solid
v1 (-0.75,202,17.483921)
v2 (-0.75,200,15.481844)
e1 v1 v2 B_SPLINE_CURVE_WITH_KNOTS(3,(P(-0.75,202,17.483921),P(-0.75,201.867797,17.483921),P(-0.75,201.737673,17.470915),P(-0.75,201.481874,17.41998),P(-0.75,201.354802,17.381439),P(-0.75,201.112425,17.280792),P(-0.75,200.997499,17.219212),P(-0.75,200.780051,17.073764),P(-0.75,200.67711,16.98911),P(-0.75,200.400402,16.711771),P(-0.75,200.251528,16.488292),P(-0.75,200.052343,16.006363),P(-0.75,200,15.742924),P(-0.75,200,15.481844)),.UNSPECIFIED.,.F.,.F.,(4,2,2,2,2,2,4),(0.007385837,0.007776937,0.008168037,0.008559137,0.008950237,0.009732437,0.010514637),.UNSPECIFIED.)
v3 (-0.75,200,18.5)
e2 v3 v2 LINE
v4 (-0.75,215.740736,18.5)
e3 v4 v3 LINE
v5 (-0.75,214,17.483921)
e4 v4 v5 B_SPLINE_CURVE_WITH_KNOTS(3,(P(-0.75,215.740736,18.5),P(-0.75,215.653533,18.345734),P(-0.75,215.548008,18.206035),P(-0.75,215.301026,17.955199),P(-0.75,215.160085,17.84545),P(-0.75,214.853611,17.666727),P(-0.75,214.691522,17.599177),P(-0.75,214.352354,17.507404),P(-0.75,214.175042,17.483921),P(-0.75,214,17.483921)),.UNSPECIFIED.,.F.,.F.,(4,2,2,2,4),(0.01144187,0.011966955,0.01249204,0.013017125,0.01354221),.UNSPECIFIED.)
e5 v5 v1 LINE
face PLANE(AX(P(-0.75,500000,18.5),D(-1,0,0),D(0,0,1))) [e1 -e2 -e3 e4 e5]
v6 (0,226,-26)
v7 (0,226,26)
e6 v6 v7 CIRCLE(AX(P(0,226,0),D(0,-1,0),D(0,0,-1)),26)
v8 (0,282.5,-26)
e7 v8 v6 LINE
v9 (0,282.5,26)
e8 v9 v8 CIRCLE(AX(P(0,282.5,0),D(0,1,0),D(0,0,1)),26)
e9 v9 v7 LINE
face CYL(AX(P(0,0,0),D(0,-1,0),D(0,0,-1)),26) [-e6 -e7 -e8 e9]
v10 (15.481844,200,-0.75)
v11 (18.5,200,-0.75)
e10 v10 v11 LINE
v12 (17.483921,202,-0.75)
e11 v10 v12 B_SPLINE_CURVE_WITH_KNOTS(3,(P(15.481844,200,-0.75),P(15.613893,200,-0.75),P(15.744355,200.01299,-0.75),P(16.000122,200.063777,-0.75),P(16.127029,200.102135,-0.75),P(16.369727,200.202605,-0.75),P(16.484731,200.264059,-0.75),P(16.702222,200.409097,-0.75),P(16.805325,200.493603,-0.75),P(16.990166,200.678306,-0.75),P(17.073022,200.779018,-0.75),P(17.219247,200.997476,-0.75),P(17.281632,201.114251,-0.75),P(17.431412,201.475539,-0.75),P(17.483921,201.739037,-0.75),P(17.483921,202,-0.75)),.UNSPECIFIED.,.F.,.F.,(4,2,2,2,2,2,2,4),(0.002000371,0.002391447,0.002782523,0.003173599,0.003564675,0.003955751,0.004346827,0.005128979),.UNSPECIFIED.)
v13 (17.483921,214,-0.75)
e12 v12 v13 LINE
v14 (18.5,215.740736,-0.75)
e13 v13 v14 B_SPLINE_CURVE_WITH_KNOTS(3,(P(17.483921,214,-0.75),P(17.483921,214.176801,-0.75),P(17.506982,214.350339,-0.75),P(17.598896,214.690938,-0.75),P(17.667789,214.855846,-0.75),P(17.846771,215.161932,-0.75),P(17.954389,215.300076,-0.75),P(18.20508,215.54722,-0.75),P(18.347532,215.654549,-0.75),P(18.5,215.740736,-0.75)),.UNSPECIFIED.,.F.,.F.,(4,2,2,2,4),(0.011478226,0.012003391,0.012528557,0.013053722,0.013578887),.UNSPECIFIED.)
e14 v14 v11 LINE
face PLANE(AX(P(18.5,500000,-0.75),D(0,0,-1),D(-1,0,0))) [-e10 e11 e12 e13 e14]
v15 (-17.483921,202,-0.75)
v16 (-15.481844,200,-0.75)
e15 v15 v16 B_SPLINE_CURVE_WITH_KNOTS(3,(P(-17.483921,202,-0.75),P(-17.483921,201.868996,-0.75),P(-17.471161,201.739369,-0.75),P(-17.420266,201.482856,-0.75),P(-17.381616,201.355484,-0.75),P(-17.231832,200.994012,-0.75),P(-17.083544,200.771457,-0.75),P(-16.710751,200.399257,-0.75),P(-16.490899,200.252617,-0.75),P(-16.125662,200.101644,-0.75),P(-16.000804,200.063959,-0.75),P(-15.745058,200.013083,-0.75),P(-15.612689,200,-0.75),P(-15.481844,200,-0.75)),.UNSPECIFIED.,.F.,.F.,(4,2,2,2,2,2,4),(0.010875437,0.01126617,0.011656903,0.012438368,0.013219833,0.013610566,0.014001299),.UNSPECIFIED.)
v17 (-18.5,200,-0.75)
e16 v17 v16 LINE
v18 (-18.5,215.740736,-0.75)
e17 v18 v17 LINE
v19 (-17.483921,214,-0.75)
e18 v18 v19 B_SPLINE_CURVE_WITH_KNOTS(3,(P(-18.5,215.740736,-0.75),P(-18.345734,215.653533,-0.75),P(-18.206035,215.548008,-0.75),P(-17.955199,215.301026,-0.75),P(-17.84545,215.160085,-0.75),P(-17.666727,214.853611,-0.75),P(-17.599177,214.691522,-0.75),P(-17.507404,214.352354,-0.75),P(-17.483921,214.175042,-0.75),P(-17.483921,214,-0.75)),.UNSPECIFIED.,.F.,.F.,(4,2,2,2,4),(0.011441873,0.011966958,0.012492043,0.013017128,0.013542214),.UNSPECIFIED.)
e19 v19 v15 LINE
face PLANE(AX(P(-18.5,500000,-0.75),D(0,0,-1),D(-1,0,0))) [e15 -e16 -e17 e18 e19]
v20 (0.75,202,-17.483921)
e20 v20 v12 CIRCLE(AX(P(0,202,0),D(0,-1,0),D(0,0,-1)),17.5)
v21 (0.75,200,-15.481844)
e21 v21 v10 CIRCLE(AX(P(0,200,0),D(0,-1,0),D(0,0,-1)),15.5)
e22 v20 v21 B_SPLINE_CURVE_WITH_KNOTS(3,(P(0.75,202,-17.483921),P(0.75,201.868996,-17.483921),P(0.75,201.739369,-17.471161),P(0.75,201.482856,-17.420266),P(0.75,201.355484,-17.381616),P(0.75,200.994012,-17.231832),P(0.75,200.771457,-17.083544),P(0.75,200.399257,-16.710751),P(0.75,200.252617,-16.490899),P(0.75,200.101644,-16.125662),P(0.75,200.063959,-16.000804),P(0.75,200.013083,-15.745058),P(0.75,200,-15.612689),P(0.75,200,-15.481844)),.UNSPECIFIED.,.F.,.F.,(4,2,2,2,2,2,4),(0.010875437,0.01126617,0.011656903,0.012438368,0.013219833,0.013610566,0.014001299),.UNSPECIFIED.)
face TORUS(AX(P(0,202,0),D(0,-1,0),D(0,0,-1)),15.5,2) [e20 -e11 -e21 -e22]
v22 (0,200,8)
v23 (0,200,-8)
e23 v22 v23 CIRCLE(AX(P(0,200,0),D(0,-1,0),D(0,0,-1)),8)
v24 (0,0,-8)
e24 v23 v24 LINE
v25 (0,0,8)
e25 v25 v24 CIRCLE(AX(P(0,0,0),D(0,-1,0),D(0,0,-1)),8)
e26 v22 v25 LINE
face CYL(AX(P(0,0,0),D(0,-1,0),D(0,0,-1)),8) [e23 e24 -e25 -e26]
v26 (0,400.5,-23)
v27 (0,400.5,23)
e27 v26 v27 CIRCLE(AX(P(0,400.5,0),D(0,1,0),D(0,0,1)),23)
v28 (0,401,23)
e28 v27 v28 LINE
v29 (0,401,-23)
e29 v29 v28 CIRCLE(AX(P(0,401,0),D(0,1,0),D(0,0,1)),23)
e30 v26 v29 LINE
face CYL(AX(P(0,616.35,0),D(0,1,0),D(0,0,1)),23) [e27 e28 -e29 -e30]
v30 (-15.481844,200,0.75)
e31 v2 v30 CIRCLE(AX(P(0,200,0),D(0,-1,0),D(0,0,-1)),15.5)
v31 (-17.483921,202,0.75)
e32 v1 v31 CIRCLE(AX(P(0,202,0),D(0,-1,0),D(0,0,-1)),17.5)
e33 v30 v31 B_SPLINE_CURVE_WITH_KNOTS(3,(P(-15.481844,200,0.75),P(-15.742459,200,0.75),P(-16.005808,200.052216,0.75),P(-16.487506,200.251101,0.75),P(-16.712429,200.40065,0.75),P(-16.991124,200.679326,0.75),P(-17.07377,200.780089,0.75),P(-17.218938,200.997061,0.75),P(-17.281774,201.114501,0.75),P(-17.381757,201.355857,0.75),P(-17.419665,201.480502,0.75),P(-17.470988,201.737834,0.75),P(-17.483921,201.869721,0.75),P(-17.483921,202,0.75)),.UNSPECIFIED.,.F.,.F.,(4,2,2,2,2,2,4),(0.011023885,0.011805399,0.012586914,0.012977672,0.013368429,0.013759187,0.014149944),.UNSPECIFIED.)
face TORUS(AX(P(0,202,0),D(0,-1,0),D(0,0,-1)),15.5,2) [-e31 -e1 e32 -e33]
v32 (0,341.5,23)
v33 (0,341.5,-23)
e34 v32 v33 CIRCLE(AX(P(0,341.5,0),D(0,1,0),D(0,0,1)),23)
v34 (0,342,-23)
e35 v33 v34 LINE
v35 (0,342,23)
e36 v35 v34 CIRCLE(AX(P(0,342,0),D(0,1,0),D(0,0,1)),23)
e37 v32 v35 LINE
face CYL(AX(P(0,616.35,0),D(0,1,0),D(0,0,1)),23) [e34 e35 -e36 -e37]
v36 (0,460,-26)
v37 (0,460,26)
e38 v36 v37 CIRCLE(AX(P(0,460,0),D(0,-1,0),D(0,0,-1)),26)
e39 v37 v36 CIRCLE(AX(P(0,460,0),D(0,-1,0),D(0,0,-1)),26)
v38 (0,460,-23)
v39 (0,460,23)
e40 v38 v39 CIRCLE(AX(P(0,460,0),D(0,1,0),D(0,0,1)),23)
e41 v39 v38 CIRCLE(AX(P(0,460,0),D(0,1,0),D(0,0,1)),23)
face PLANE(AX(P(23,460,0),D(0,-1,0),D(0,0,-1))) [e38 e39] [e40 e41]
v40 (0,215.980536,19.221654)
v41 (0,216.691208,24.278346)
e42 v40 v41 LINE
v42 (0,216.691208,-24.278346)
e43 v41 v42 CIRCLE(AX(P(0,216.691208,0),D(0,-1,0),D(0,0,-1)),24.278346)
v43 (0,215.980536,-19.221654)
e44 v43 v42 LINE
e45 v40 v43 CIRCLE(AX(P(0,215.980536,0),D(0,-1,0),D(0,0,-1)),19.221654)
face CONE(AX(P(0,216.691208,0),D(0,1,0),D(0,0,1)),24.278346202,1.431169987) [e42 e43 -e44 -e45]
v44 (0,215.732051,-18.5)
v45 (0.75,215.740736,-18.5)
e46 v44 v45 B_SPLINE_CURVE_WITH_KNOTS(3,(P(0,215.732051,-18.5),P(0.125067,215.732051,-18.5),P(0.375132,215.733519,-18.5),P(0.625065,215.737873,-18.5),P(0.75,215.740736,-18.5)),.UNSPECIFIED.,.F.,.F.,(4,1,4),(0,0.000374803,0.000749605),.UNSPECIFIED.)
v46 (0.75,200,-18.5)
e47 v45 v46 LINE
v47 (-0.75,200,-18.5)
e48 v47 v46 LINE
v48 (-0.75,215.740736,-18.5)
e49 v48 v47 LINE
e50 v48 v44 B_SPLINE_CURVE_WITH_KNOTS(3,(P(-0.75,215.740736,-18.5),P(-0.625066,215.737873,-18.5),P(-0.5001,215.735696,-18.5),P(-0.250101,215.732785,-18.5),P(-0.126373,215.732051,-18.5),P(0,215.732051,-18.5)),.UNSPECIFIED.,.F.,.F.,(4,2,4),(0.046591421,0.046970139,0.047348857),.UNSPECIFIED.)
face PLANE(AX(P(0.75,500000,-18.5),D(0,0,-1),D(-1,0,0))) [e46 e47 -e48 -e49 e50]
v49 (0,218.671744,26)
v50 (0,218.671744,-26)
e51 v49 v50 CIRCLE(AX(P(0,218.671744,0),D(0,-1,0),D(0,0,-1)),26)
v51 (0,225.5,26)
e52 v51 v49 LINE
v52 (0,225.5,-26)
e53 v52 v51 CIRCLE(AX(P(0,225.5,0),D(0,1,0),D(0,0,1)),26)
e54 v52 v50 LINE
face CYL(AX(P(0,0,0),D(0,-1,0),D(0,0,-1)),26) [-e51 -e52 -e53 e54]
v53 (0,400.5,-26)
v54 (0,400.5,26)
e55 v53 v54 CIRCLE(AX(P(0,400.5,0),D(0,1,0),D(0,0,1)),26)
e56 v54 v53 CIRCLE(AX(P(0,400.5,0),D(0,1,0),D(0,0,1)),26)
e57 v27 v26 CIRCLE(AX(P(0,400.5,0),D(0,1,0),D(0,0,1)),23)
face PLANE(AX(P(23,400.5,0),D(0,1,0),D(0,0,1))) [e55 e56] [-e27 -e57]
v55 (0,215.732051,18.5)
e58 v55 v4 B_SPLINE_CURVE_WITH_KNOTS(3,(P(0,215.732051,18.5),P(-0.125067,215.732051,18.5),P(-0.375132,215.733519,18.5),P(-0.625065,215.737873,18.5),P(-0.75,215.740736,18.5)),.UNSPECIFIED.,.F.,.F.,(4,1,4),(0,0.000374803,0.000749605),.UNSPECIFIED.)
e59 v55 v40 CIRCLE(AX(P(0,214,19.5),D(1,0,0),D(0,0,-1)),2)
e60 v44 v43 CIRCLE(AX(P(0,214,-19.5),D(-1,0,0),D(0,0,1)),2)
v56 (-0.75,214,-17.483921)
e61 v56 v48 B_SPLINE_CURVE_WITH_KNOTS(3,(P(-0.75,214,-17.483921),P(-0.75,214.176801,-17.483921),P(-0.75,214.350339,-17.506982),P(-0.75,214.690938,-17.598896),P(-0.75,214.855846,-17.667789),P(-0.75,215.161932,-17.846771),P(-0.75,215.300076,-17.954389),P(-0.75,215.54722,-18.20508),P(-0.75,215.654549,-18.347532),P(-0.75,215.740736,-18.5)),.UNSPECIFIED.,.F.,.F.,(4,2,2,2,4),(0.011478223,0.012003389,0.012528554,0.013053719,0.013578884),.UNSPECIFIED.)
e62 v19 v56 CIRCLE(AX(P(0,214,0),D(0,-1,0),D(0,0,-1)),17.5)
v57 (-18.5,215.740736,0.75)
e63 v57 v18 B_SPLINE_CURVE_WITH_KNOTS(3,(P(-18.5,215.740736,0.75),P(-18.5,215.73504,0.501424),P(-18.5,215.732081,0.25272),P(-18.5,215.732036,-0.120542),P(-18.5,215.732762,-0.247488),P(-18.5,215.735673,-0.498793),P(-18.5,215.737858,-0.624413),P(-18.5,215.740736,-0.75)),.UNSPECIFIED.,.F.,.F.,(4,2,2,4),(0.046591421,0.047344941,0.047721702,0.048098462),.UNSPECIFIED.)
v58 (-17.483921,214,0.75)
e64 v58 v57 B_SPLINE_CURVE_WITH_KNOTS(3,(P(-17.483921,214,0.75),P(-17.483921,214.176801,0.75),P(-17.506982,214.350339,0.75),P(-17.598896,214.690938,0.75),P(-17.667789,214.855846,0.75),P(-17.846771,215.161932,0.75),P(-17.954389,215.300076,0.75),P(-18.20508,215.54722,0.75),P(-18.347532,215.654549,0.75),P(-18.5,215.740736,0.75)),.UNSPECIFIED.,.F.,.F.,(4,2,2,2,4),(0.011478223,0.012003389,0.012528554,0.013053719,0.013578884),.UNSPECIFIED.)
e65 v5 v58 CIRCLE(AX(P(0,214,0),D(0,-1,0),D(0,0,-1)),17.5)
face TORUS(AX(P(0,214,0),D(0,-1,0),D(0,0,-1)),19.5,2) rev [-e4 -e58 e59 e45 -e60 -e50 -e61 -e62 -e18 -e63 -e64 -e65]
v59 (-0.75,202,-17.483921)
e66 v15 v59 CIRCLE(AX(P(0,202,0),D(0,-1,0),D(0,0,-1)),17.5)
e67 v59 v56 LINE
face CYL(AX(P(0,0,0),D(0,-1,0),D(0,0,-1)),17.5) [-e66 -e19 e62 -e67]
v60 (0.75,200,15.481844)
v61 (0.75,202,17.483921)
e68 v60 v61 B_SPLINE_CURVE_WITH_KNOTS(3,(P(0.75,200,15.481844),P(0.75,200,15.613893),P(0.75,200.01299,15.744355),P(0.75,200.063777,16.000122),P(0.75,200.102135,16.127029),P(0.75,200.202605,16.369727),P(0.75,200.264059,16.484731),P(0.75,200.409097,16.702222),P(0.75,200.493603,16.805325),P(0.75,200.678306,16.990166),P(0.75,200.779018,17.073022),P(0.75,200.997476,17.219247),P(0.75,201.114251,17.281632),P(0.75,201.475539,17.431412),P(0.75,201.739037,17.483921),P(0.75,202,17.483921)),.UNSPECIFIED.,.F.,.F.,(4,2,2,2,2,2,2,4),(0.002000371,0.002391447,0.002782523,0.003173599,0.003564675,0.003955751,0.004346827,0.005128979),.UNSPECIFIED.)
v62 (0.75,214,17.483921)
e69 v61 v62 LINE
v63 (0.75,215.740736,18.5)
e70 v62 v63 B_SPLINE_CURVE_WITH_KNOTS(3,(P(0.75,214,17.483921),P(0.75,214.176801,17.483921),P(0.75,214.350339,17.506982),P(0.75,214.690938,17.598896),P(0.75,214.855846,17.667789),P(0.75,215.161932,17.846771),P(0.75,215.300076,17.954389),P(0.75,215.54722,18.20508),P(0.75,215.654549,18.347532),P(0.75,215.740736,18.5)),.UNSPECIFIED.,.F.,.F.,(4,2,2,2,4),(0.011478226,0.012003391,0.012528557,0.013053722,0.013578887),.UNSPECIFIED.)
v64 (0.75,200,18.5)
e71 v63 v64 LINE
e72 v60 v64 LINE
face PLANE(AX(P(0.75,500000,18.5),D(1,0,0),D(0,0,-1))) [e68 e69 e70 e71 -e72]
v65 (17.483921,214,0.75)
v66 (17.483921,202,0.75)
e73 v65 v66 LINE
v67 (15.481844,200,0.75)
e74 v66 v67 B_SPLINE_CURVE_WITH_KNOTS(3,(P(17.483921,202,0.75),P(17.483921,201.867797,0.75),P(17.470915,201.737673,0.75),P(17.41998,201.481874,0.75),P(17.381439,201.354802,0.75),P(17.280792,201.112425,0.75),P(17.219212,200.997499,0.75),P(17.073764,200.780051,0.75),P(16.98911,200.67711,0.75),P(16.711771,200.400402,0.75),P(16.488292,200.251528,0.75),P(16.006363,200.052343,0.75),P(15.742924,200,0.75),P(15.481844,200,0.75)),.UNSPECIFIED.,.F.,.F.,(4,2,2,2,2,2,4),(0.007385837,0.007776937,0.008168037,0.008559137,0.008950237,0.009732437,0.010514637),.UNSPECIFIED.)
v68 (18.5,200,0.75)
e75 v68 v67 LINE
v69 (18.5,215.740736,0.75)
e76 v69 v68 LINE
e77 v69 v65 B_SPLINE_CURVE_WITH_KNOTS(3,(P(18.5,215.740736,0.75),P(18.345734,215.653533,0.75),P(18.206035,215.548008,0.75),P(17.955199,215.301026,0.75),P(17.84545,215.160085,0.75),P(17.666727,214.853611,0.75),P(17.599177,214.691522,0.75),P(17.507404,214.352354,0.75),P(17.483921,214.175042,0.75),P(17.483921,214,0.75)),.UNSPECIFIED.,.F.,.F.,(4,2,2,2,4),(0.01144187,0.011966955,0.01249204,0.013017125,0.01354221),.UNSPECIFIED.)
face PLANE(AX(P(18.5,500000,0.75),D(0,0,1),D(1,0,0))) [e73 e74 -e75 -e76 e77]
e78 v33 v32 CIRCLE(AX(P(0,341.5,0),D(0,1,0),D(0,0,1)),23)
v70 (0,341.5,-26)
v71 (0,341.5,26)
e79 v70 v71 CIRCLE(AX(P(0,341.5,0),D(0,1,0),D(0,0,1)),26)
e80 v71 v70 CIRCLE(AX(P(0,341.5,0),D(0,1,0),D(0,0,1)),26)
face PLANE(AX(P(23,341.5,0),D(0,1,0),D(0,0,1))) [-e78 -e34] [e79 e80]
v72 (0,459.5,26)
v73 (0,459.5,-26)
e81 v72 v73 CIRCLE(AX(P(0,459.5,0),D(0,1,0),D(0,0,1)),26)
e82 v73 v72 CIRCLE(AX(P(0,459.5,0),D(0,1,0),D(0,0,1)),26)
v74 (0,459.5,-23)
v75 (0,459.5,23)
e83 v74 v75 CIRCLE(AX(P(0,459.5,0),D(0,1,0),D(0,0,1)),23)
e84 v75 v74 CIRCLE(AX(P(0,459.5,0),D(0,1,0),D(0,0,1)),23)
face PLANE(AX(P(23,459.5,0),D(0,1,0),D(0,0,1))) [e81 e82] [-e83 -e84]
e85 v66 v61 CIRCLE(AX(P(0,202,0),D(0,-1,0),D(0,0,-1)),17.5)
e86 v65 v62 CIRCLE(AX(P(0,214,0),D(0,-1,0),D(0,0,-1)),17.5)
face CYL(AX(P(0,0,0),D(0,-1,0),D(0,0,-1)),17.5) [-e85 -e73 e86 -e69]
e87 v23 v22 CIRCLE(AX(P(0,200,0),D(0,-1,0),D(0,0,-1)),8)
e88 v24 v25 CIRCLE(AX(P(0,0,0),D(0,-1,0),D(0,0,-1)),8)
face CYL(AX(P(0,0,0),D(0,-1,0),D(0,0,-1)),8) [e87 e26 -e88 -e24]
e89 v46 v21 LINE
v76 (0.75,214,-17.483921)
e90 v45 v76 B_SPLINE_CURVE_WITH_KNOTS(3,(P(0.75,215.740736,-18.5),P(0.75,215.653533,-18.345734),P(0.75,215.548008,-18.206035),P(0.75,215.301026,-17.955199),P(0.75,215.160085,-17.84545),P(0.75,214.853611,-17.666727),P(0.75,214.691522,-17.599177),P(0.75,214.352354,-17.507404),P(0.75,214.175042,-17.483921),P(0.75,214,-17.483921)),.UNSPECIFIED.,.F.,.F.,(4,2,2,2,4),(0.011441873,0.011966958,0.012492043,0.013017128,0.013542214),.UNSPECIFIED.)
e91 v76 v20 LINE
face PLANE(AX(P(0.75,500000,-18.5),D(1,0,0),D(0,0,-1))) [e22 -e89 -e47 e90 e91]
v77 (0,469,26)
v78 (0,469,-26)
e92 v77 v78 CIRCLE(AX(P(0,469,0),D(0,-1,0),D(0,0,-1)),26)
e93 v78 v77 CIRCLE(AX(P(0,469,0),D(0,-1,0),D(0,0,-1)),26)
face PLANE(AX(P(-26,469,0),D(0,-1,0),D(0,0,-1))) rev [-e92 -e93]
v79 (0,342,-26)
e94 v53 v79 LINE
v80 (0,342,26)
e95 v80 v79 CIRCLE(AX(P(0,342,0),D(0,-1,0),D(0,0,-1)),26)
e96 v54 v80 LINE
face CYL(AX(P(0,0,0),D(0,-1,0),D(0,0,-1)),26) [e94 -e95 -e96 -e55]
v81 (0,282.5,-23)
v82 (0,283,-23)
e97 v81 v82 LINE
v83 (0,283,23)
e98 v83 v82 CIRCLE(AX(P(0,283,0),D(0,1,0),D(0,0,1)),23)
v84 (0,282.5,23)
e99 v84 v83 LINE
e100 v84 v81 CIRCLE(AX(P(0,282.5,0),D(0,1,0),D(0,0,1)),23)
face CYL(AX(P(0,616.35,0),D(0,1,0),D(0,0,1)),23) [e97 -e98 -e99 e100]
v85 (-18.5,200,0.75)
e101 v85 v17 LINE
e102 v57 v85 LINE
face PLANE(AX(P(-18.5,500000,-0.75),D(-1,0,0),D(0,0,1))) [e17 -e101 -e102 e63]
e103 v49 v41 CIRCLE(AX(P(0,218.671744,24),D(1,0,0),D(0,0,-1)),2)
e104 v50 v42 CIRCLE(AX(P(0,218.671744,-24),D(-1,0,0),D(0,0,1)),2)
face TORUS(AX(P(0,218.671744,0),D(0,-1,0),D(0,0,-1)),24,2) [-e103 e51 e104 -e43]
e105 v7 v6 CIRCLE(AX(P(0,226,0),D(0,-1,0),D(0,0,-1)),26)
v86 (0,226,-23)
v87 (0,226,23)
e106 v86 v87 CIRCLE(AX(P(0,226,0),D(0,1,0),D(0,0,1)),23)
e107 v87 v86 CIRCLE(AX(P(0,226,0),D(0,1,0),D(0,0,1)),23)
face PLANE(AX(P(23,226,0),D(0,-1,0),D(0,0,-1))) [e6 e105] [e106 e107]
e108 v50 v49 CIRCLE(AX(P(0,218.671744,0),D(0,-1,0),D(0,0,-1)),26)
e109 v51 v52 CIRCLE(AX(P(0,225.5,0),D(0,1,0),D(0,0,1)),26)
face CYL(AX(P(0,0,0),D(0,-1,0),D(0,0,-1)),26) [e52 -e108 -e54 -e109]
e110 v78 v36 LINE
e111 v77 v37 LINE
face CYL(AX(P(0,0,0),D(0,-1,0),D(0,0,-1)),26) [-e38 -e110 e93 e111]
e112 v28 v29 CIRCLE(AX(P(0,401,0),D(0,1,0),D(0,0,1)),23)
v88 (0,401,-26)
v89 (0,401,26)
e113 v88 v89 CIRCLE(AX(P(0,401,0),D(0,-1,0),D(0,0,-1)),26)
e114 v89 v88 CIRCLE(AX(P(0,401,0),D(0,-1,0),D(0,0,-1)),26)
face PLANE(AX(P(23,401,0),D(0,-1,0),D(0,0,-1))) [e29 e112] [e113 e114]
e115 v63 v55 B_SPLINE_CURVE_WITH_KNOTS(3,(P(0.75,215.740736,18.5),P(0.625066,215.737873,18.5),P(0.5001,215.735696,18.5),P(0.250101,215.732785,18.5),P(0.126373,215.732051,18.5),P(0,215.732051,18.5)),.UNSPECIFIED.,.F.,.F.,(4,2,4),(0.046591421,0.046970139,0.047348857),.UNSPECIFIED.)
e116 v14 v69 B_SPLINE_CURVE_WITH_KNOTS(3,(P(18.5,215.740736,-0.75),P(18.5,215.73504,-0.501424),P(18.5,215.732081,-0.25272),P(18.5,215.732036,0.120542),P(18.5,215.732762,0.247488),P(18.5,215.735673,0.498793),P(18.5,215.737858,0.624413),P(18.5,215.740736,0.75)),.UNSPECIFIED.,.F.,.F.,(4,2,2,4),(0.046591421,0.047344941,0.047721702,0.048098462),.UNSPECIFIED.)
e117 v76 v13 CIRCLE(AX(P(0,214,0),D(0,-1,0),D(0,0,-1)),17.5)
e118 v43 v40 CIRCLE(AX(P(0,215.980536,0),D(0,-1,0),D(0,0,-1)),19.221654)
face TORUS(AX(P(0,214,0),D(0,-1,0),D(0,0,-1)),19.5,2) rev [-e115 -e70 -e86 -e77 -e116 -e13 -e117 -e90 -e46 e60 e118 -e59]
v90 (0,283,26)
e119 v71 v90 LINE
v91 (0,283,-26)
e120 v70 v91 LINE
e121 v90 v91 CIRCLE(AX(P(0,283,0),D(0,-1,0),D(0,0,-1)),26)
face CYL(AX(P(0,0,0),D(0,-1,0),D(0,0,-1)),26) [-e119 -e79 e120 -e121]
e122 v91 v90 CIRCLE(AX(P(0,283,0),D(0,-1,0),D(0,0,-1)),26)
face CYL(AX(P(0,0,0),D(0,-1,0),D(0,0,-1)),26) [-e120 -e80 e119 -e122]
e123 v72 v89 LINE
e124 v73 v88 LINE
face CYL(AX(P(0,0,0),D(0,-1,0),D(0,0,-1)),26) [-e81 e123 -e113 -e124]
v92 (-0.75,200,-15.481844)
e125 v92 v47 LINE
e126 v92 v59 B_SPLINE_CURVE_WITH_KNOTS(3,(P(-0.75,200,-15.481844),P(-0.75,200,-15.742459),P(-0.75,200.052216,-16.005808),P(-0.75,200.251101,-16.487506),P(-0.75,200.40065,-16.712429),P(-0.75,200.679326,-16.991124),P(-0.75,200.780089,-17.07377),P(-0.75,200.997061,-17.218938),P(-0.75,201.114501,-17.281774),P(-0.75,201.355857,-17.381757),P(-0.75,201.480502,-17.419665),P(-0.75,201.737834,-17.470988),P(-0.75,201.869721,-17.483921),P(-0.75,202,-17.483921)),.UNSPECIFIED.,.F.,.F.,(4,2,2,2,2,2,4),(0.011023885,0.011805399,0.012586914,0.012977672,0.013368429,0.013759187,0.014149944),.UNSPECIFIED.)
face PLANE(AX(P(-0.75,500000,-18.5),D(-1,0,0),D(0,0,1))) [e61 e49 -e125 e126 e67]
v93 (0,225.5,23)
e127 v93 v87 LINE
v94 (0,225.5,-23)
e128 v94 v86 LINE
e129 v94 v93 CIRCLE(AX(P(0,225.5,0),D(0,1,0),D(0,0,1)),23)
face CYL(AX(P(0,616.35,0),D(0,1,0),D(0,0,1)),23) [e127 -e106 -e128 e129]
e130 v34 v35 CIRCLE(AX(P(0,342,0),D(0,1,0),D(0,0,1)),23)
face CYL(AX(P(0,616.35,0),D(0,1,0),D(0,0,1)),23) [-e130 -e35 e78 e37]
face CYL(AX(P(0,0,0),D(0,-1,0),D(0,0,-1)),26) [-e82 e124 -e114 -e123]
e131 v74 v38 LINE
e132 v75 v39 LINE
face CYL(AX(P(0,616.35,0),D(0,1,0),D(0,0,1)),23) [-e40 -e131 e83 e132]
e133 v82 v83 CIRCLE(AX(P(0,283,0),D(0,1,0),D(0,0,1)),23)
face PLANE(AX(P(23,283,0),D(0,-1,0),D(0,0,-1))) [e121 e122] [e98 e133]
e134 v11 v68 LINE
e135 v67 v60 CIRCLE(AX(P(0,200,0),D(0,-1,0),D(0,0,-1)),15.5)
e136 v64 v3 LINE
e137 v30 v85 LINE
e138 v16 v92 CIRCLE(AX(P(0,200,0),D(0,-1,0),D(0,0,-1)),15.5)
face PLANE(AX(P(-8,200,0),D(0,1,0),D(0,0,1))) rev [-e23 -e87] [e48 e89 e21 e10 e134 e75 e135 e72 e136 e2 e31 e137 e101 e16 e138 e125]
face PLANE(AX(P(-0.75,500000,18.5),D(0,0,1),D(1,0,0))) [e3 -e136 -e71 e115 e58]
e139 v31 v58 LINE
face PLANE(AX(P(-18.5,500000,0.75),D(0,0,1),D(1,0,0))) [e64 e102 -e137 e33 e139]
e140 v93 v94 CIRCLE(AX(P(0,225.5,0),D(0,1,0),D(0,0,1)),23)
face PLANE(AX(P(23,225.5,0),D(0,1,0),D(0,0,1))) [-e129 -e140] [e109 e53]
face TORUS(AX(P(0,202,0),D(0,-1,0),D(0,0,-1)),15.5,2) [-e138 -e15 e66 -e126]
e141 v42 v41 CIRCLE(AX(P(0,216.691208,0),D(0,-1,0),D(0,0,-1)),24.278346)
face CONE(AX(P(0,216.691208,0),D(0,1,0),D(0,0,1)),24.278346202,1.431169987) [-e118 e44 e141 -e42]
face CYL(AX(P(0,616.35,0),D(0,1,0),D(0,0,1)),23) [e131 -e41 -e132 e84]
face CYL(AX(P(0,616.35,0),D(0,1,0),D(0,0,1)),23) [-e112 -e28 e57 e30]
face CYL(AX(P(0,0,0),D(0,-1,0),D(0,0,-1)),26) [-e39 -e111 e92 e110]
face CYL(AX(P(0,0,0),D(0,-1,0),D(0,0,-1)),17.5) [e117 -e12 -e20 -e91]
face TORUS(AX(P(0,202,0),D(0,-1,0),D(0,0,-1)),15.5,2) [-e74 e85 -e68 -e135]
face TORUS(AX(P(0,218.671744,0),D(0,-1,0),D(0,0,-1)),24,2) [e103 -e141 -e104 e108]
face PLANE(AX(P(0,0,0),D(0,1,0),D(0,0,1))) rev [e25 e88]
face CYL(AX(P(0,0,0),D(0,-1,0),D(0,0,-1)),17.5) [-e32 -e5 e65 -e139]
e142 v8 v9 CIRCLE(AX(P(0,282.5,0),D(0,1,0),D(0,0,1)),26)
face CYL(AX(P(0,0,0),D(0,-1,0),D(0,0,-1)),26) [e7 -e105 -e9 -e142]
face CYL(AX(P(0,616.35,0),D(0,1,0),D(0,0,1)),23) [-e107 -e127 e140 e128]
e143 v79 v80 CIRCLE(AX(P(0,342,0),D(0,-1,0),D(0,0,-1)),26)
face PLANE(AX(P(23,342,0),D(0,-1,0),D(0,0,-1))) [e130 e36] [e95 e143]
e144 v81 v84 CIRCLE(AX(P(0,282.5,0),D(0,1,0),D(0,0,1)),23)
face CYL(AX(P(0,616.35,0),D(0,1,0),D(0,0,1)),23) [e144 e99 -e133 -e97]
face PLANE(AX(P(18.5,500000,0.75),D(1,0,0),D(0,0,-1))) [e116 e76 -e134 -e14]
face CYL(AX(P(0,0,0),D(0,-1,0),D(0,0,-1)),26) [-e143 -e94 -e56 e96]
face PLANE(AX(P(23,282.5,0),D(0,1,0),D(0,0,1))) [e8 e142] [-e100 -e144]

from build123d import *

# Parameters (mm, degrees)
SKETCH_2_W      = 6
SKETCH_2_H      = 0.5
EXTRUDE_1_REACH = 273.501
SKETCH_3_W      = 6
SKETCH_3_H      = 1.5
SKETCH_3_W_2    = 1.5
SKETCH_3_H_2    = 6


with BuildPart() as part:
    # 草图1 → 旋转1 (revolve)
    with BuildSketch(Plane.XY, mode=Mode.PRIVATE) as revolve_1_sk:
        with BuildLine():
            Line((0, 0), (-8, 0))
            Line((-8, 0), (-8, 200))
            Line((-8, 200), (-15.5, 200))
            ThreePointArc((-15.5, 200), (-16.914213562, 200.585786438), (-17.5, 202))
            Line((-17.5, 202), (-17.5, 214))
            ThreePointArc((-17.5, 214), (-17.99058084, 215.312118058), (-19.221653798, 215.980536137))
            Line((-19.221653798, 215.980536137), (-24.278346202, 216.691207909))
            ThreePointArc((-24.278346202, 216.691207909), (-25.50941916, 217.359625988), (-26, 218.671744046))
            Line((-26, 218.671744046), (-26, 469))
            Line((-26, 469), (0, 469))
            Line((0, 469), (0, 0))
        make_face()
    revolve(revolve_1_sk.sketch.rotate(Axis((0, 0, 0), (0, 1, 0)), 270), axis=Axis((0, 0, 0), (0, 1, 0)))

    # 草图2 → 切除-旋转1 (revolve, cut)
    with BuildSketch(Plane.XY, mode=Mode.PRIVATE) as cut_revolve_1_sk:
        with Locations((26, 225.75)):
            Rectangle(SKETCH_2_W, SKETCH_2_H)
        with Locations((26, 282.75)):
            Rectangle(SKETCH_2_W, SKETCH_2_H)
        with Locations((26, 341.75)):
            Rectangle(SKETCH_2_W, SKETCH_2_H)
        with Locations((26, 400.75)):
            Rectangle(SKETCH_2_W, SKETCH_2_H)
        with Locations((26, 459.75)):
            Rectangle(SKETCH_2_W, SKETCH_2_H)
        with Locations((26, 518.75)):
            Rectangle(SKETCH_2_W, SKETCH_2_H)
        with Locations((26, 577.75)):
            Rectangle(SKETCH_2_W, SKETCH_2_H)
    revolve(cut_revolve_1_sk.sketch.rotate(Axis((0, 616.35, 0), (0, -1, 0)), 270), axis=Axis((0, 616.35, 0), (0, -1, 0)), mode=Mode.SUBTRACT)

    # 草图3 → 凸台-拉伸1 (add, up to next)
    with BuildSketch(Plane.XZ.offset(-200), mode=Mode.PRIVATE) as extrude_1_sk1:
        with Locations((15.5, 0)):
            Rectangle(SKETCH_3_W, SKETCH_3_H)
    extrude_1_tool1 = extrude(extrude_1_sk1.sketch, amount=-EXTRUDE_1_REACH, mode=Mode.PRIVATE) - part.part
    # 草图3 → 凸台-拉伸1 (add, up to next)
    with BuildSketch(Plane.XZ.offset(-200), mode=Mode.PRIVATE) as extrude_1_sk2:
        with Locations((0, 15.5)):
            Rectangle(SKETCH_3_W_2, SKETCH_3_H_2)
    extrude_1_tool2 = extrude(extrude_1_sk2.sketch, amount=-EXTRUDE_1_REACH, mode=Mode.PRIVATE) - part.part
    # 草图3 → 凸台-拉伸1 (add, up to next)
    with BuildSketch(Plane.XZ.offset(-200), mode=Mode.PRIVATE) as extrude_1_sk3:
        with Locations((0, -15.5)):
            Rectangle(SKETCH_3_W_2, SKETCH_3_H_2)
    extrude_1_tool3 = extrude(extrude_1_sk3.sketch, amount=-EXTRUDE_1_REACH, mode=Mode.PRIVATE) - part.part
    # 草图3 → 凸台-拉伸1 (add, up to next)
    with BuildSketch(Plane.XZ.offset(-200), mode=Mode.PRIVATE) as extrude_1_sk4:
        with Locations((-15.5, 0)):
            Rectangle(SKETCH_3_W, SKETCH_3_H)
    extrude_1_tool4 = extrude(extrude_1_sk4.sketch, amount=-EXTRUDE_1_REACH, mode=Mode.PRIVATE) - part.part
    add(extrude_1_tool1.solids().sort_by_distance((15.5, 200, 0))[0])
    add(extrude_1_tool2.solids().sort_by_distance((0, 200, 15.5))[0])
    add(extrude_1_tool3.solids().sort_by_distance((0, 200, -15.5))[0])
    add(extrude_1_tool4.solids().sort_by_distance((-15.5, 200, 0))[0])


solid = part.part
